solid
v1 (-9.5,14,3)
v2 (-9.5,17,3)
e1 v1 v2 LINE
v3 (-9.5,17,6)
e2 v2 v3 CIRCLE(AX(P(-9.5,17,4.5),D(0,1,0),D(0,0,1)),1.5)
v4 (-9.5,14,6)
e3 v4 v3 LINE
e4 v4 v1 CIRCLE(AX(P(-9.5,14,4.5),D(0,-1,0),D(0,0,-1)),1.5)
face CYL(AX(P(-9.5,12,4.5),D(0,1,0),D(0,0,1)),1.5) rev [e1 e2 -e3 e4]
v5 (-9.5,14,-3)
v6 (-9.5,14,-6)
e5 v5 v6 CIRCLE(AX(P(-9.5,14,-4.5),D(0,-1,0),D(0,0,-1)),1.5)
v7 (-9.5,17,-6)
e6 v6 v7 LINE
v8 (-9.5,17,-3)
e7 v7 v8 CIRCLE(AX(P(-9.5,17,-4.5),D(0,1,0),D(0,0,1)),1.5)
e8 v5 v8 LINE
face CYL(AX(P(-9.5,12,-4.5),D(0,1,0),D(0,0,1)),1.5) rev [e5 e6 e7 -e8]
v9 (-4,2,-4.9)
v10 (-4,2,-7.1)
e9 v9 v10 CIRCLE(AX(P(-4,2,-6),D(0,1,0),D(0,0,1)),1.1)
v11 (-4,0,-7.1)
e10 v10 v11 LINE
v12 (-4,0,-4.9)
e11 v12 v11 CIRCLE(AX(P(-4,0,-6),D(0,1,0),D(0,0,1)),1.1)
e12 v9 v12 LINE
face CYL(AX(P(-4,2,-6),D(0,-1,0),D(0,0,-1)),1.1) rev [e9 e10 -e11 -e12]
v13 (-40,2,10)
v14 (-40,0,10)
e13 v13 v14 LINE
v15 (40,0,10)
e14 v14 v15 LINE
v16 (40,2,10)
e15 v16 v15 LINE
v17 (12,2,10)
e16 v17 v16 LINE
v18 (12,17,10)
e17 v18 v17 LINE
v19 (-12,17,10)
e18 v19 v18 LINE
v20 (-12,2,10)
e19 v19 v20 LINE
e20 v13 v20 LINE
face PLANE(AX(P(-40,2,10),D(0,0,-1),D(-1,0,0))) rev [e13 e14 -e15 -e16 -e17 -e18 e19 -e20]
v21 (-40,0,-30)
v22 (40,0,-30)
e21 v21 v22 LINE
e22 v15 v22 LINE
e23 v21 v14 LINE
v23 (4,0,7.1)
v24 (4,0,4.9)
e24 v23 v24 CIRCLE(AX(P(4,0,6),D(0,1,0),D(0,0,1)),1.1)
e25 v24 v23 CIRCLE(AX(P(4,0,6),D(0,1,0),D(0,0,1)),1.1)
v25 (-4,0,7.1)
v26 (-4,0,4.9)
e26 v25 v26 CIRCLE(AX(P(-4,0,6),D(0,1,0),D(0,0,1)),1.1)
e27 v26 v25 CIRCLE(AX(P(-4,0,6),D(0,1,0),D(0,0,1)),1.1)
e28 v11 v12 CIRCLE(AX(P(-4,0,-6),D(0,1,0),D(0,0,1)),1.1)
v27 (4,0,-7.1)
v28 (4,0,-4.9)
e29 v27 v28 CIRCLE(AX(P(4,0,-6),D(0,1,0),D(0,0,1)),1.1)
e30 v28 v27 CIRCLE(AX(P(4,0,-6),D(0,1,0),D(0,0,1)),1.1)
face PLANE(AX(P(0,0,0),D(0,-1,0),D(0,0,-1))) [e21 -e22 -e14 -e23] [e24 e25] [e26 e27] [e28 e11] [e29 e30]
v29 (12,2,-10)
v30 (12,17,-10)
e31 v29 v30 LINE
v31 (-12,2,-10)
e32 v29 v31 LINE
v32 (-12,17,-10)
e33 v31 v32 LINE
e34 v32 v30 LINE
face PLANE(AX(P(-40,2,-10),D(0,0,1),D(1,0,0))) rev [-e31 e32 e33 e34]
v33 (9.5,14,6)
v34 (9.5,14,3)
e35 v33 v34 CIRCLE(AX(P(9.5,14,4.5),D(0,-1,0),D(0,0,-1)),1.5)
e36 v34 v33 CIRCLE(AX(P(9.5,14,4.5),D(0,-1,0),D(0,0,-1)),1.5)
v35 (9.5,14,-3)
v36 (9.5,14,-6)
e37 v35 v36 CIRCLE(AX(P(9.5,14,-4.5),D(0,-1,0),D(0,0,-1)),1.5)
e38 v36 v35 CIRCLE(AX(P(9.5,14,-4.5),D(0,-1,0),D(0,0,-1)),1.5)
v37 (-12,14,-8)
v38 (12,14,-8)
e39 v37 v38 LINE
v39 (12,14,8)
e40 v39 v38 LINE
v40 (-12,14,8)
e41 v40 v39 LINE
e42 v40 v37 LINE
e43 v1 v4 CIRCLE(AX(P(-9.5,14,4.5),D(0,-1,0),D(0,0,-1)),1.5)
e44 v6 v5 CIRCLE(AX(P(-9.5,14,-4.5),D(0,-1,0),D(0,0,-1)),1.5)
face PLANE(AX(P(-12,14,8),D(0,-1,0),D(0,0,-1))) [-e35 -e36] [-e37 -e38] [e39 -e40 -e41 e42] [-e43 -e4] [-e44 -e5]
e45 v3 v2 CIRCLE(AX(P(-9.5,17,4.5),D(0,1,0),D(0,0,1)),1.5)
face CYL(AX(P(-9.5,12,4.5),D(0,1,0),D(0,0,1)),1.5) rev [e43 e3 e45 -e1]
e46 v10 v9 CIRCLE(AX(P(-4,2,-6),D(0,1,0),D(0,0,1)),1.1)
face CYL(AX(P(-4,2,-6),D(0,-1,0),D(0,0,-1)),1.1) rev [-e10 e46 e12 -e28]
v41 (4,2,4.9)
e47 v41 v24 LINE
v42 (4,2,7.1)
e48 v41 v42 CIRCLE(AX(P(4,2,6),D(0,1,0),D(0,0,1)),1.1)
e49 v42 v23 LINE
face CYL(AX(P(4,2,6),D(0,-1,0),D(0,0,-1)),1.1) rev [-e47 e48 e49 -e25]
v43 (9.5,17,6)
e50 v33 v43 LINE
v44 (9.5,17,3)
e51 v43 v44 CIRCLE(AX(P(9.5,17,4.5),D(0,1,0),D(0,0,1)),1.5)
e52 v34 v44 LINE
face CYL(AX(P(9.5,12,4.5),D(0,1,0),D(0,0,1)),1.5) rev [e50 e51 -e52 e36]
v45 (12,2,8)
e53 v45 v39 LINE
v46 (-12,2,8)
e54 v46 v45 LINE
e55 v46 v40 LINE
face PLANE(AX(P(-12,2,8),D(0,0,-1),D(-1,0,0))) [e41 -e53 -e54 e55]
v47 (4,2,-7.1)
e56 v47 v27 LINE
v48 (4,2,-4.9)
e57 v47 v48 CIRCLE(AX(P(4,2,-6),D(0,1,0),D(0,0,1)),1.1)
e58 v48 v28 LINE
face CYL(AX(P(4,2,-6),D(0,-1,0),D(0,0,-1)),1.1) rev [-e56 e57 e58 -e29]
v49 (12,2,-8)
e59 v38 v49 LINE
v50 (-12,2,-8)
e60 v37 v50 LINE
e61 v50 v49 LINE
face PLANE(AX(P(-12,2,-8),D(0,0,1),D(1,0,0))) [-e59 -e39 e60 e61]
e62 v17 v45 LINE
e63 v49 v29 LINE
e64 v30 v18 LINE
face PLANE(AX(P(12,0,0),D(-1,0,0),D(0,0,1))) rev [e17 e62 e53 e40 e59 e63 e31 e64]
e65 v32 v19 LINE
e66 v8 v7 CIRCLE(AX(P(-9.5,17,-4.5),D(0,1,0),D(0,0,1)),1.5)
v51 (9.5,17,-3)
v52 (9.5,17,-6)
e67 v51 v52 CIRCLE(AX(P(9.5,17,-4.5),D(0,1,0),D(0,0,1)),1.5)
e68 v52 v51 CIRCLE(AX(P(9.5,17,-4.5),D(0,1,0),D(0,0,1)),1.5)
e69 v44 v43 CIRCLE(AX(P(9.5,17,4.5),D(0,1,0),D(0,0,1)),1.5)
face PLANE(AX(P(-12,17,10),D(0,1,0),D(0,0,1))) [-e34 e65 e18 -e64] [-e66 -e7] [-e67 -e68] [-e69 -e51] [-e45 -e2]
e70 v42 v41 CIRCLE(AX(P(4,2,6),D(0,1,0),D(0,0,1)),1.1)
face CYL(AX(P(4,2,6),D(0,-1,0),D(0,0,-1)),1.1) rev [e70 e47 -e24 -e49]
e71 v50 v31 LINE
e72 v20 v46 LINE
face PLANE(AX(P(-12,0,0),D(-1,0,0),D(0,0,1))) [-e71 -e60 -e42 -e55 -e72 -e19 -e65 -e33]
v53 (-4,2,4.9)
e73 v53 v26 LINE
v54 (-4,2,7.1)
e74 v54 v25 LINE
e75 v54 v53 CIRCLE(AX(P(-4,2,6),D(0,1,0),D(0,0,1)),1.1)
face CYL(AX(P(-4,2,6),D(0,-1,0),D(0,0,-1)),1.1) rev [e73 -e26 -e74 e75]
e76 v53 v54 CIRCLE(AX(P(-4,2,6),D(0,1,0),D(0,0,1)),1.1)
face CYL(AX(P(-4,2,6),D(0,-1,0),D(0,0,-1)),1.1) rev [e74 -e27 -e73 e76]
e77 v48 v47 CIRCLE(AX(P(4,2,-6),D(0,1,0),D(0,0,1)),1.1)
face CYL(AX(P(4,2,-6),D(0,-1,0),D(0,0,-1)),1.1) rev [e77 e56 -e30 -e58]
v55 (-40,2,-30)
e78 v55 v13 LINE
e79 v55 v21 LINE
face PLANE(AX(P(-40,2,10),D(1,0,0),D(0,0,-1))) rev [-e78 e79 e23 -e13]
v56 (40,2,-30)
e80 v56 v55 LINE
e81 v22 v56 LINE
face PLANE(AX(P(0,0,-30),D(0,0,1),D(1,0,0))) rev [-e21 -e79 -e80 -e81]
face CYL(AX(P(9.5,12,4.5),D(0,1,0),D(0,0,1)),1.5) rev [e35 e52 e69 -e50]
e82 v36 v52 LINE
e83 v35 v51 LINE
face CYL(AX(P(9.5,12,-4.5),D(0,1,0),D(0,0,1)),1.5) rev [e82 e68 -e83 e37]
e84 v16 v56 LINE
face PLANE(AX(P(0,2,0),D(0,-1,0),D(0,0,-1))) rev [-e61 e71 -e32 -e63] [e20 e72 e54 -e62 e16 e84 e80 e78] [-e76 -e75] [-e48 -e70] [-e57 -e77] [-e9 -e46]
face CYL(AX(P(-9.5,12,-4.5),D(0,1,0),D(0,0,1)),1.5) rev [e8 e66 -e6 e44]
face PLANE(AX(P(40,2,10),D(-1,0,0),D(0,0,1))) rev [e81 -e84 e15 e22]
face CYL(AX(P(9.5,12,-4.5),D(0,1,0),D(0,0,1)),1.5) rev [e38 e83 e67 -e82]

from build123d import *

# Parameters (mm, degrees)
SKETCH1_W           = 80
SKETCH1_H           = 20
SKETCH1_R           = 1.1
BOSS_EXTRUDE1_DEPTH = 2
BOSS_EXTRUDE3_DEPTH = 12
SKETCH4_R           = 1.5
CUT_EXTRUDE1_DEPTH  = 5
SKETCH5_W           = 80
SKETCH5_H           = 2
BOSS_EXTRUDE4_DEPTH = 20


with BuildPart() as part:
    # Sketch1 → Boss-Extrude1 (new body)
    with BuildSketch(Plane(origin=(0, 0, 0), x_dir=(1, 0, 0), z_dir=(0, 1, 0))):
        Rectangle(SKETCH1_W, SKETCH1_H)
        with Locations(Location((-4, 6, 0), (0, 0, 270))):
            Circle(SKETCH1_R, mode=Mode.SUBTRACT)
        with Locations(Location((4, 6, 0), (0, 0, 270))):
            Circle(SKETCH1_R, mode=Mode.SUBTRACT)
        with Locations(Location((-4, -6, 0), (0, 0, 270))):
            Circle(SKETCH1_R, mode=Mode.SUBTRACT)
        with Locations(Location((4, -6, 0), (0, 0, 270))):
            Circle(SKETCH1_R, mode=Mode.SUBTRACT)
    extrude(amount=BOSS_EXTRUDE1_DEPTH)

    # Sketch3 → Boss-Extrude3 (add, symmetric)
    with BuildSketch(Plane(origin=(0, 0, 0), x_dir=(0, 0, -1), z_dir=(1, 0, 0))):
        Polygon((-10, 2), (-8, 2), (-8, 14), (8, 14), (8, 2), (10, 2), (10, 13.782871327), (10, 17), (-10, 17), (-10, 13.782871327), align=None)
    extrude(amount=BOSS_EXTRUDE3_DEPTH, both=True)

    # Sketch4 → Cut-Extrude1 (cut)
    with BuildSketch(Plane(origin=(0, 17, 0), x_dir=(1, 0, 0), z_dir=(0, 1, 0))):
        with Locations(Location((9.5, -4.5, 0), (0, 0, 270))):
            Circle(SKETCH4_R)
        with Locations(Location((-9.5, -4.5, 0), (0, 0, 270))):
            Circle(SKETCH4_R)
        with Locations(Location((-9.5, 4.5, 0), (0, 0, 270))):
            Circle(SKETCH4_R)
        with Locations(Location((9.5, 4.5, 0), (0, 0, 270))):
            Circle(SKETCH4_R)
    extrude(amount=-CUT_EXTRUDE1_DEPTH, mode=Mode.SUBTRACT)

    # Sketch5 → Boss-Extrude4 (add)
    with BuildSketch(Plane.XY.offset(-10)):
        with Locations((0, 1)):
            Rectangle(SKETCH5_W, SKETCH5_H)
    extrude(amount=-BOSS_EXTRUDE4_DEPTH)


solid = part.part
